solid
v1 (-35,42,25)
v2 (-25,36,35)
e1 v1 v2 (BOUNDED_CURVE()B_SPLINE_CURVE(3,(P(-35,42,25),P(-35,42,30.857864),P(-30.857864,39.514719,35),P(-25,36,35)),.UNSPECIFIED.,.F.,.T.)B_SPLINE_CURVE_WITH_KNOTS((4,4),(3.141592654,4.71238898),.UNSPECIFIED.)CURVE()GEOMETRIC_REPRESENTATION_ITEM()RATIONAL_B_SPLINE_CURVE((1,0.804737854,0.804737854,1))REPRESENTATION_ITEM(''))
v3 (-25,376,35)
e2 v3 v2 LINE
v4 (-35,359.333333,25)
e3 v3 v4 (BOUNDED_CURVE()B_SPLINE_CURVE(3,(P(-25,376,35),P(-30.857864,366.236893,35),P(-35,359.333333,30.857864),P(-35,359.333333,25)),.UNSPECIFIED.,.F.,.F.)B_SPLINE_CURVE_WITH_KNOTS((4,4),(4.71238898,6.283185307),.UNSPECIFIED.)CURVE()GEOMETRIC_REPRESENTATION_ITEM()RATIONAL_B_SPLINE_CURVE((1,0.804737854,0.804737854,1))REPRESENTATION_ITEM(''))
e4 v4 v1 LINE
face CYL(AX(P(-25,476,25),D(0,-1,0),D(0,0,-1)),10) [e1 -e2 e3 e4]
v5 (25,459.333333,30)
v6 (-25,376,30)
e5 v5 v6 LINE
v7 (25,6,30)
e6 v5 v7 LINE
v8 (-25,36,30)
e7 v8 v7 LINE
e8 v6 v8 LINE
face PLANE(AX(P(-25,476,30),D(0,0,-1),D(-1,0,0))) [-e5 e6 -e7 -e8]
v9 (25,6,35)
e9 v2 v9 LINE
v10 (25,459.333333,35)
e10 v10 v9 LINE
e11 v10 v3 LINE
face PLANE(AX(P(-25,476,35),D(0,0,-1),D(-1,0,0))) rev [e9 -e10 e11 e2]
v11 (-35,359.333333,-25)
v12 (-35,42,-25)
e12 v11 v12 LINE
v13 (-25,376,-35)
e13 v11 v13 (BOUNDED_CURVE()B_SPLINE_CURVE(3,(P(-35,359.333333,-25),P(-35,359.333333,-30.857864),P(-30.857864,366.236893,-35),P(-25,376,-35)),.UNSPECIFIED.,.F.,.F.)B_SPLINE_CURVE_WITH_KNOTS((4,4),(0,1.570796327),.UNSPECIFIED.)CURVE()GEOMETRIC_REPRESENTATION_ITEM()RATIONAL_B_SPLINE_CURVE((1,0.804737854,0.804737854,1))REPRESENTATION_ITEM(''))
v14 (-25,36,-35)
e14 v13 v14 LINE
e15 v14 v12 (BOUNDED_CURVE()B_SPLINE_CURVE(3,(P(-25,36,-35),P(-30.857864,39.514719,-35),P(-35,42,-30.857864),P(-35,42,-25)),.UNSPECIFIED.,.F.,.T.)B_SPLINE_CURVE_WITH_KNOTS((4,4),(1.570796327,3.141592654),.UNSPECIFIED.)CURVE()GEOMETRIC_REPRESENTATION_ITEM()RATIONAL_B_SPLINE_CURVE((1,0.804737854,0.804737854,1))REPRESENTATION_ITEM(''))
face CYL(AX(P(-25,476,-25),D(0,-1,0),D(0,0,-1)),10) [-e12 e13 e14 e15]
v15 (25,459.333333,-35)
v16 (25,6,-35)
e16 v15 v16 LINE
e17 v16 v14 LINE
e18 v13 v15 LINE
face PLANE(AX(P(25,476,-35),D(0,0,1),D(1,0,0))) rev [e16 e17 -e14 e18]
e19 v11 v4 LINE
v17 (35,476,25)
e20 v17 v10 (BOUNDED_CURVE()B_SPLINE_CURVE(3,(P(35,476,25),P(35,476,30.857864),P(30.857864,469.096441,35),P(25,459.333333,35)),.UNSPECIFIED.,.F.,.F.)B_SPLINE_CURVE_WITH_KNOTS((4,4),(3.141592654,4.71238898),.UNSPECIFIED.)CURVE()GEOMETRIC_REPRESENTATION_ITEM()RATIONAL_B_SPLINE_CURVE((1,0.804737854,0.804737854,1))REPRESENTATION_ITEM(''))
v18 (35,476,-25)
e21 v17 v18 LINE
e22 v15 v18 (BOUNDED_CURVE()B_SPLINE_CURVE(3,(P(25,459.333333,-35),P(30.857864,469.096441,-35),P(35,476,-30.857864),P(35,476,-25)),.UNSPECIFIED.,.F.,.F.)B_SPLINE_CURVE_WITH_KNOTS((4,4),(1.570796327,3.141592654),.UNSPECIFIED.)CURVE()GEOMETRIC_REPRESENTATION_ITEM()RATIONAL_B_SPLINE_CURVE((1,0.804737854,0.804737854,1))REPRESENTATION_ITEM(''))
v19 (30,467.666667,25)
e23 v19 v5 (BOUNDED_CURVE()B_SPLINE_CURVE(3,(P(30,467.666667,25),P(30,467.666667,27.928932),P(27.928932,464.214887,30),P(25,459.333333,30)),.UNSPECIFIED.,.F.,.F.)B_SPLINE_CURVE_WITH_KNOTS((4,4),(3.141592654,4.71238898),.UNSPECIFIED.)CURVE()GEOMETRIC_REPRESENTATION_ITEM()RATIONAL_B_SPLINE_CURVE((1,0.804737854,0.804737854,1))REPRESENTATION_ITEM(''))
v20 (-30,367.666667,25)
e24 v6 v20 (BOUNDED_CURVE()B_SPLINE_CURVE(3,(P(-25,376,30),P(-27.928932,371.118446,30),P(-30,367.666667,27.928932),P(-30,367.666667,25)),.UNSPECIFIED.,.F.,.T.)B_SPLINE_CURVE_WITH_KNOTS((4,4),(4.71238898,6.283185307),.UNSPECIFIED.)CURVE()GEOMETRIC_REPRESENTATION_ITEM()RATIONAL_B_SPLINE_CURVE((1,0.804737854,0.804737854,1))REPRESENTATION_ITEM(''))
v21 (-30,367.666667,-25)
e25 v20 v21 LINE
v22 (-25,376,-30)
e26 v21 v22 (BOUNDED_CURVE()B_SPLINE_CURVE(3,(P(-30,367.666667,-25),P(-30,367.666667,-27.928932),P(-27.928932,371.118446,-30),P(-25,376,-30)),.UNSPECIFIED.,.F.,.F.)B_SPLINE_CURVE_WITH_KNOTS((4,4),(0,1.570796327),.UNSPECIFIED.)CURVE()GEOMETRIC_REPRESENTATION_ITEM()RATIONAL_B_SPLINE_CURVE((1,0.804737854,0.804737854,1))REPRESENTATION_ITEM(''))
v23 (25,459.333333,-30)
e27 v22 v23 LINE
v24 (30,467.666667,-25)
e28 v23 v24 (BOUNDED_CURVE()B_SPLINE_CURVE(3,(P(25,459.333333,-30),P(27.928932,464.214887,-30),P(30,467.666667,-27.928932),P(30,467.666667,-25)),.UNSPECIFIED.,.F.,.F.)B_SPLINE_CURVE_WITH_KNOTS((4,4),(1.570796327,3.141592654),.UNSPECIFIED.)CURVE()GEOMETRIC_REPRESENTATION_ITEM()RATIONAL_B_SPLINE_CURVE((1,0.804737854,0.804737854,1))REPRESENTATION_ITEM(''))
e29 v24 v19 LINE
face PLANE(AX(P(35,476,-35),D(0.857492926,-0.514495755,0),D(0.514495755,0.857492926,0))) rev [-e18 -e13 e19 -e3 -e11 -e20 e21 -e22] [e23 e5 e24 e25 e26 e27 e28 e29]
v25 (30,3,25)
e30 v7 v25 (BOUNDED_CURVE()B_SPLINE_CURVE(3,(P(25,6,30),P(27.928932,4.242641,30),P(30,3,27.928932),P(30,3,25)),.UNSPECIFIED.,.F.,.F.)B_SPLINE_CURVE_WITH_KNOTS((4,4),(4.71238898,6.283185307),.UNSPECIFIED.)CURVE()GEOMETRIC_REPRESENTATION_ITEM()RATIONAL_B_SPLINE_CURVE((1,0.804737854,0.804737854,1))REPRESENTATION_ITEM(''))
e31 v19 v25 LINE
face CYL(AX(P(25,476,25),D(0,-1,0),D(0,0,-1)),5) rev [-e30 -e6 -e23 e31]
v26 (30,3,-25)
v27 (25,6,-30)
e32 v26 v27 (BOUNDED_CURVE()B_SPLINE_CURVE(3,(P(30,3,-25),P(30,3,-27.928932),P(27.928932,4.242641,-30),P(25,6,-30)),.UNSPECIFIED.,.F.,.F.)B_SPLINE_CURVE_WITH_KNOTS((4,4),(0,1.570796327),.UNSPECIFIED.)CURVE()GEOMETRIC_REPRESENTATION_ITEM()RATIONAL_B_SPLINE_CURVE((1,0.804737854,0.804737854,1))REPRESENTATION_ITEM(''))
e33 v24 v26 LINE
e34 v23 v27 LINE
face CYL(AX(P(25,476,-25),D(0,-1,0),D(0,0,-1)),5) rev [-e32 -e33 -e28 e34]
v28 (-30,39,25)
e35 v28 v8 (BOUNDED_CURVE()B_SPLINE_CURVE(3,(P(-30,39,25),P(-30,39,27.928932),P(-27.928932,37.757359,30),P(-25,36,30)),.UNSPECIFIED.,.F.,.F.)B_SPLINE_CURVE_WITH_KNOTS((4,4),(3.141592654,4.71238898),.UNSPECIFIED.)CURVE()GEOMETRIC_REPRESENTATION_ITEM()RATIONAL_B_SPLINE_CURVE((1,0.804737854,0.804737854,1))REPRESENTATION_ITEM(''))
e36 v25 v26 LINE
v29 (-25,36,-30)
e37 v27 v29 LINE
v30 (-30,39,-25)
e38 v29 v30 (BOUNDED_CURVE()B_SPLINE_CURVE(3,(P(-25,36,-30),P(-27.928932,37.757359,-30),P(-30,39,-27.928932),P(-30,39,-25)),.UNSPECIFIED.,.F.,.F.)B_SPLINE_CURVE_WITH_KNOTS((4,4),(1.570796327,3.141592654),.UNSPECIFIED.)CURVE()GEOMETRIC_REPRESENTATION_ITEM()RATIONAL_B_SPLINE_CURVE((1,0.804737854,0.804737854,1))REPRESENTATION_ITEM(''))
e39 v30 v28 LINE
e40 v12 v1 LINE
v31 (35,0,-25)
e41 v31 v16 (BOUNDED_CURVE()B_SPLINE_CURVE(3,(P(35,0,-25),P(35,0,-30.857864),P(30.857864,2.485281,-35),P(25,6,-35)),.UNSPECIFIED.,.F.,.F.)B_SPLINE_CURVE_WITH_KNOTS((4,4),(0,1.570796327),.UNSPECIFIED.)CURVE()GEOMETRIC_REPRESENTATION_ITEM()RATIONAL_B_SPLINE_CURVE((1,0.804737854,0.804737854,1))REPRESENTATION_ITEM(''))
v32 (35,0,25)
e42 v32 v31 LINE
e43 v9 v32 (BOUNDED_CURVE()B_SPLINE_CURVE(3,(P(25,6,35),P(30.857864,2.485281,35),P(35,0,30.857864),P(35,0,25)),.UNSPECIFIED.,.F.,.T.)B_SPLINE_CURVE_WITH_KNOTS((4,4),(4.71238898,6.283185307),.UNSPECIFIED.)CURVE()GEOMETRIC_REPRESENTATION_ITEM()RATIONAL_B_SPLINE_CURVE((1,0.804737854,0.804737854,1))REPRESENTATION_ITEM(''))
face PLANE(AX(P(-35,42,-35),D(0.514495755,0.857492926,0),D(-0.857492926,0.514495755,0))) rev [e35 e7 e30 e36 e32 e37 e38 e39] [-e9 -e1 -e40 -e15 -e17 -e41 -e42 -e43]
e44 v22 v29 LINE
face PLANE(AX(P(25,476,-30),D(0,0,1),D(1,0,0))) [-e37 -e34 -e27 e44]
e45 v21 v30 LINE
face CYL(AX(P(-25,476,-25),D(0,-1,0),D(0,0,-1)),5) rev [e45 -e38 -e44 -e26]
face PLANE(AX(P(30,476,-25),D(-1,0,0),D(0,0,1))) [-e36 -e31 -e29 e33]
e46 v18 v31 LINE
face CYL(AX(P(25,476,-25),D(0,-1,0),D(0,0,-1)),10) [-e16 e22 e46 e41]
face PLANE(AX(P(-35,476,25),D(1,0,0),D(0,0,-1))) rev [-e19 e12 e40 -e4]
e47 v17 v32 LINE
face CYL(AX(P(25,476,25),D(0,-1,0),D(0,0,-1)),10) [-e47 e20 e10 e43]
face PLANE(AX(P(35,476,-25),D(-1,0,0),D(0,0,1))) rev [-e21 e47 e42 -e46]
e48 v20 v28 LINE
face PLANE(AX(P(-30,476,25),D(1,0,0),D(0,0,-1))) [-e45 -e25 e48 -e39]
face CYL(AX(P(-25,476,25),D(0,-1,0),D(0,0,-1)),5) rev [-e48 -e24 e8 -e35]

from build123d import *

# Parameters (mm, degrees)
GB_T6728_2002_70_70_5_1_DEPTH = 476
CUT_EXTRUDE_1_DEPTH           = 483.390920313
CUT_EXTRUDE_1_DEPTH_BACK      = 483.390920313


with BuildPart() as part:
    # Sketch1 → 结构用冷弯空心方钢(gb t6728-2002) 70×70×5(1) (new body)
    with BuildSketch(Plane(origin=(0, 0, 0), x_dir=(-1, 0, 0), z_dir=(0, 1, 0))):
        with BuildLine():
            Line((-25, -35), (25, -35))
            ThreePointArc((25, -35), (32.071067812, -32.071067812), (35, -25))
            Line((35, -25), (35, 25))
            ThreePointArc((35, 25), (32.071067812, 32.071067812), (25, 35))
            Line((25, 35), (-25, 35))
            ThreePointArc((-25, 35), (-32.071067812, 32.071067812), (-35, 25))
            Line((-35, 25), (-35, -25))
            ThreePointArc((-35, -25), (-32.071067812, -32.071067812), (-25, -35))
        make_face()
        with BuildLine():
            Line((-25, -30), (25, -30))
            ThreePointArc((25, -30), (28.535533906, -28.535533906), (30, -25))
            Line((30, -25), (30, 25))
            ThreePointArc((30, 25), (28.535533906, 28.535533906), (25, 30))
            Line((25, 30), (-25, 30))
            ThreePointArc((-25, 30), (-28.535533906, 28.535533906), (-30, 25))
            Line((-30, 25), (-30, -25))
            ThreePointArc((-30, -25), (-28.535533906, -28.535533906), (-25, -30))
        make_face(mode=Mode.SUBTRACT)
    extrude(amount=GB_T6728_2002_70_70_5_1_DEPTH)

    # 草图2 → 切除-拉伸1 (cut, two sides: drawn at the far end of the back side and taken through both)
    with BuildSketch(Plane.XY.offset(35).offset(-CUT_EXTRUDE_1_DEPTH_BACK)):
        Polygon((35, 476), (-35, 359.333333333), (-35, 476), align=None)
        Polygon((-35, 42), (35, 0), (-35, 0), align=None)
    extrude(amount=CUT_EXTRUDE_1_DEPTH + CUT_EXTRUDE_1_DEPTH_BACK, mode=Mode.SUBTRACT)


solid = part.part
